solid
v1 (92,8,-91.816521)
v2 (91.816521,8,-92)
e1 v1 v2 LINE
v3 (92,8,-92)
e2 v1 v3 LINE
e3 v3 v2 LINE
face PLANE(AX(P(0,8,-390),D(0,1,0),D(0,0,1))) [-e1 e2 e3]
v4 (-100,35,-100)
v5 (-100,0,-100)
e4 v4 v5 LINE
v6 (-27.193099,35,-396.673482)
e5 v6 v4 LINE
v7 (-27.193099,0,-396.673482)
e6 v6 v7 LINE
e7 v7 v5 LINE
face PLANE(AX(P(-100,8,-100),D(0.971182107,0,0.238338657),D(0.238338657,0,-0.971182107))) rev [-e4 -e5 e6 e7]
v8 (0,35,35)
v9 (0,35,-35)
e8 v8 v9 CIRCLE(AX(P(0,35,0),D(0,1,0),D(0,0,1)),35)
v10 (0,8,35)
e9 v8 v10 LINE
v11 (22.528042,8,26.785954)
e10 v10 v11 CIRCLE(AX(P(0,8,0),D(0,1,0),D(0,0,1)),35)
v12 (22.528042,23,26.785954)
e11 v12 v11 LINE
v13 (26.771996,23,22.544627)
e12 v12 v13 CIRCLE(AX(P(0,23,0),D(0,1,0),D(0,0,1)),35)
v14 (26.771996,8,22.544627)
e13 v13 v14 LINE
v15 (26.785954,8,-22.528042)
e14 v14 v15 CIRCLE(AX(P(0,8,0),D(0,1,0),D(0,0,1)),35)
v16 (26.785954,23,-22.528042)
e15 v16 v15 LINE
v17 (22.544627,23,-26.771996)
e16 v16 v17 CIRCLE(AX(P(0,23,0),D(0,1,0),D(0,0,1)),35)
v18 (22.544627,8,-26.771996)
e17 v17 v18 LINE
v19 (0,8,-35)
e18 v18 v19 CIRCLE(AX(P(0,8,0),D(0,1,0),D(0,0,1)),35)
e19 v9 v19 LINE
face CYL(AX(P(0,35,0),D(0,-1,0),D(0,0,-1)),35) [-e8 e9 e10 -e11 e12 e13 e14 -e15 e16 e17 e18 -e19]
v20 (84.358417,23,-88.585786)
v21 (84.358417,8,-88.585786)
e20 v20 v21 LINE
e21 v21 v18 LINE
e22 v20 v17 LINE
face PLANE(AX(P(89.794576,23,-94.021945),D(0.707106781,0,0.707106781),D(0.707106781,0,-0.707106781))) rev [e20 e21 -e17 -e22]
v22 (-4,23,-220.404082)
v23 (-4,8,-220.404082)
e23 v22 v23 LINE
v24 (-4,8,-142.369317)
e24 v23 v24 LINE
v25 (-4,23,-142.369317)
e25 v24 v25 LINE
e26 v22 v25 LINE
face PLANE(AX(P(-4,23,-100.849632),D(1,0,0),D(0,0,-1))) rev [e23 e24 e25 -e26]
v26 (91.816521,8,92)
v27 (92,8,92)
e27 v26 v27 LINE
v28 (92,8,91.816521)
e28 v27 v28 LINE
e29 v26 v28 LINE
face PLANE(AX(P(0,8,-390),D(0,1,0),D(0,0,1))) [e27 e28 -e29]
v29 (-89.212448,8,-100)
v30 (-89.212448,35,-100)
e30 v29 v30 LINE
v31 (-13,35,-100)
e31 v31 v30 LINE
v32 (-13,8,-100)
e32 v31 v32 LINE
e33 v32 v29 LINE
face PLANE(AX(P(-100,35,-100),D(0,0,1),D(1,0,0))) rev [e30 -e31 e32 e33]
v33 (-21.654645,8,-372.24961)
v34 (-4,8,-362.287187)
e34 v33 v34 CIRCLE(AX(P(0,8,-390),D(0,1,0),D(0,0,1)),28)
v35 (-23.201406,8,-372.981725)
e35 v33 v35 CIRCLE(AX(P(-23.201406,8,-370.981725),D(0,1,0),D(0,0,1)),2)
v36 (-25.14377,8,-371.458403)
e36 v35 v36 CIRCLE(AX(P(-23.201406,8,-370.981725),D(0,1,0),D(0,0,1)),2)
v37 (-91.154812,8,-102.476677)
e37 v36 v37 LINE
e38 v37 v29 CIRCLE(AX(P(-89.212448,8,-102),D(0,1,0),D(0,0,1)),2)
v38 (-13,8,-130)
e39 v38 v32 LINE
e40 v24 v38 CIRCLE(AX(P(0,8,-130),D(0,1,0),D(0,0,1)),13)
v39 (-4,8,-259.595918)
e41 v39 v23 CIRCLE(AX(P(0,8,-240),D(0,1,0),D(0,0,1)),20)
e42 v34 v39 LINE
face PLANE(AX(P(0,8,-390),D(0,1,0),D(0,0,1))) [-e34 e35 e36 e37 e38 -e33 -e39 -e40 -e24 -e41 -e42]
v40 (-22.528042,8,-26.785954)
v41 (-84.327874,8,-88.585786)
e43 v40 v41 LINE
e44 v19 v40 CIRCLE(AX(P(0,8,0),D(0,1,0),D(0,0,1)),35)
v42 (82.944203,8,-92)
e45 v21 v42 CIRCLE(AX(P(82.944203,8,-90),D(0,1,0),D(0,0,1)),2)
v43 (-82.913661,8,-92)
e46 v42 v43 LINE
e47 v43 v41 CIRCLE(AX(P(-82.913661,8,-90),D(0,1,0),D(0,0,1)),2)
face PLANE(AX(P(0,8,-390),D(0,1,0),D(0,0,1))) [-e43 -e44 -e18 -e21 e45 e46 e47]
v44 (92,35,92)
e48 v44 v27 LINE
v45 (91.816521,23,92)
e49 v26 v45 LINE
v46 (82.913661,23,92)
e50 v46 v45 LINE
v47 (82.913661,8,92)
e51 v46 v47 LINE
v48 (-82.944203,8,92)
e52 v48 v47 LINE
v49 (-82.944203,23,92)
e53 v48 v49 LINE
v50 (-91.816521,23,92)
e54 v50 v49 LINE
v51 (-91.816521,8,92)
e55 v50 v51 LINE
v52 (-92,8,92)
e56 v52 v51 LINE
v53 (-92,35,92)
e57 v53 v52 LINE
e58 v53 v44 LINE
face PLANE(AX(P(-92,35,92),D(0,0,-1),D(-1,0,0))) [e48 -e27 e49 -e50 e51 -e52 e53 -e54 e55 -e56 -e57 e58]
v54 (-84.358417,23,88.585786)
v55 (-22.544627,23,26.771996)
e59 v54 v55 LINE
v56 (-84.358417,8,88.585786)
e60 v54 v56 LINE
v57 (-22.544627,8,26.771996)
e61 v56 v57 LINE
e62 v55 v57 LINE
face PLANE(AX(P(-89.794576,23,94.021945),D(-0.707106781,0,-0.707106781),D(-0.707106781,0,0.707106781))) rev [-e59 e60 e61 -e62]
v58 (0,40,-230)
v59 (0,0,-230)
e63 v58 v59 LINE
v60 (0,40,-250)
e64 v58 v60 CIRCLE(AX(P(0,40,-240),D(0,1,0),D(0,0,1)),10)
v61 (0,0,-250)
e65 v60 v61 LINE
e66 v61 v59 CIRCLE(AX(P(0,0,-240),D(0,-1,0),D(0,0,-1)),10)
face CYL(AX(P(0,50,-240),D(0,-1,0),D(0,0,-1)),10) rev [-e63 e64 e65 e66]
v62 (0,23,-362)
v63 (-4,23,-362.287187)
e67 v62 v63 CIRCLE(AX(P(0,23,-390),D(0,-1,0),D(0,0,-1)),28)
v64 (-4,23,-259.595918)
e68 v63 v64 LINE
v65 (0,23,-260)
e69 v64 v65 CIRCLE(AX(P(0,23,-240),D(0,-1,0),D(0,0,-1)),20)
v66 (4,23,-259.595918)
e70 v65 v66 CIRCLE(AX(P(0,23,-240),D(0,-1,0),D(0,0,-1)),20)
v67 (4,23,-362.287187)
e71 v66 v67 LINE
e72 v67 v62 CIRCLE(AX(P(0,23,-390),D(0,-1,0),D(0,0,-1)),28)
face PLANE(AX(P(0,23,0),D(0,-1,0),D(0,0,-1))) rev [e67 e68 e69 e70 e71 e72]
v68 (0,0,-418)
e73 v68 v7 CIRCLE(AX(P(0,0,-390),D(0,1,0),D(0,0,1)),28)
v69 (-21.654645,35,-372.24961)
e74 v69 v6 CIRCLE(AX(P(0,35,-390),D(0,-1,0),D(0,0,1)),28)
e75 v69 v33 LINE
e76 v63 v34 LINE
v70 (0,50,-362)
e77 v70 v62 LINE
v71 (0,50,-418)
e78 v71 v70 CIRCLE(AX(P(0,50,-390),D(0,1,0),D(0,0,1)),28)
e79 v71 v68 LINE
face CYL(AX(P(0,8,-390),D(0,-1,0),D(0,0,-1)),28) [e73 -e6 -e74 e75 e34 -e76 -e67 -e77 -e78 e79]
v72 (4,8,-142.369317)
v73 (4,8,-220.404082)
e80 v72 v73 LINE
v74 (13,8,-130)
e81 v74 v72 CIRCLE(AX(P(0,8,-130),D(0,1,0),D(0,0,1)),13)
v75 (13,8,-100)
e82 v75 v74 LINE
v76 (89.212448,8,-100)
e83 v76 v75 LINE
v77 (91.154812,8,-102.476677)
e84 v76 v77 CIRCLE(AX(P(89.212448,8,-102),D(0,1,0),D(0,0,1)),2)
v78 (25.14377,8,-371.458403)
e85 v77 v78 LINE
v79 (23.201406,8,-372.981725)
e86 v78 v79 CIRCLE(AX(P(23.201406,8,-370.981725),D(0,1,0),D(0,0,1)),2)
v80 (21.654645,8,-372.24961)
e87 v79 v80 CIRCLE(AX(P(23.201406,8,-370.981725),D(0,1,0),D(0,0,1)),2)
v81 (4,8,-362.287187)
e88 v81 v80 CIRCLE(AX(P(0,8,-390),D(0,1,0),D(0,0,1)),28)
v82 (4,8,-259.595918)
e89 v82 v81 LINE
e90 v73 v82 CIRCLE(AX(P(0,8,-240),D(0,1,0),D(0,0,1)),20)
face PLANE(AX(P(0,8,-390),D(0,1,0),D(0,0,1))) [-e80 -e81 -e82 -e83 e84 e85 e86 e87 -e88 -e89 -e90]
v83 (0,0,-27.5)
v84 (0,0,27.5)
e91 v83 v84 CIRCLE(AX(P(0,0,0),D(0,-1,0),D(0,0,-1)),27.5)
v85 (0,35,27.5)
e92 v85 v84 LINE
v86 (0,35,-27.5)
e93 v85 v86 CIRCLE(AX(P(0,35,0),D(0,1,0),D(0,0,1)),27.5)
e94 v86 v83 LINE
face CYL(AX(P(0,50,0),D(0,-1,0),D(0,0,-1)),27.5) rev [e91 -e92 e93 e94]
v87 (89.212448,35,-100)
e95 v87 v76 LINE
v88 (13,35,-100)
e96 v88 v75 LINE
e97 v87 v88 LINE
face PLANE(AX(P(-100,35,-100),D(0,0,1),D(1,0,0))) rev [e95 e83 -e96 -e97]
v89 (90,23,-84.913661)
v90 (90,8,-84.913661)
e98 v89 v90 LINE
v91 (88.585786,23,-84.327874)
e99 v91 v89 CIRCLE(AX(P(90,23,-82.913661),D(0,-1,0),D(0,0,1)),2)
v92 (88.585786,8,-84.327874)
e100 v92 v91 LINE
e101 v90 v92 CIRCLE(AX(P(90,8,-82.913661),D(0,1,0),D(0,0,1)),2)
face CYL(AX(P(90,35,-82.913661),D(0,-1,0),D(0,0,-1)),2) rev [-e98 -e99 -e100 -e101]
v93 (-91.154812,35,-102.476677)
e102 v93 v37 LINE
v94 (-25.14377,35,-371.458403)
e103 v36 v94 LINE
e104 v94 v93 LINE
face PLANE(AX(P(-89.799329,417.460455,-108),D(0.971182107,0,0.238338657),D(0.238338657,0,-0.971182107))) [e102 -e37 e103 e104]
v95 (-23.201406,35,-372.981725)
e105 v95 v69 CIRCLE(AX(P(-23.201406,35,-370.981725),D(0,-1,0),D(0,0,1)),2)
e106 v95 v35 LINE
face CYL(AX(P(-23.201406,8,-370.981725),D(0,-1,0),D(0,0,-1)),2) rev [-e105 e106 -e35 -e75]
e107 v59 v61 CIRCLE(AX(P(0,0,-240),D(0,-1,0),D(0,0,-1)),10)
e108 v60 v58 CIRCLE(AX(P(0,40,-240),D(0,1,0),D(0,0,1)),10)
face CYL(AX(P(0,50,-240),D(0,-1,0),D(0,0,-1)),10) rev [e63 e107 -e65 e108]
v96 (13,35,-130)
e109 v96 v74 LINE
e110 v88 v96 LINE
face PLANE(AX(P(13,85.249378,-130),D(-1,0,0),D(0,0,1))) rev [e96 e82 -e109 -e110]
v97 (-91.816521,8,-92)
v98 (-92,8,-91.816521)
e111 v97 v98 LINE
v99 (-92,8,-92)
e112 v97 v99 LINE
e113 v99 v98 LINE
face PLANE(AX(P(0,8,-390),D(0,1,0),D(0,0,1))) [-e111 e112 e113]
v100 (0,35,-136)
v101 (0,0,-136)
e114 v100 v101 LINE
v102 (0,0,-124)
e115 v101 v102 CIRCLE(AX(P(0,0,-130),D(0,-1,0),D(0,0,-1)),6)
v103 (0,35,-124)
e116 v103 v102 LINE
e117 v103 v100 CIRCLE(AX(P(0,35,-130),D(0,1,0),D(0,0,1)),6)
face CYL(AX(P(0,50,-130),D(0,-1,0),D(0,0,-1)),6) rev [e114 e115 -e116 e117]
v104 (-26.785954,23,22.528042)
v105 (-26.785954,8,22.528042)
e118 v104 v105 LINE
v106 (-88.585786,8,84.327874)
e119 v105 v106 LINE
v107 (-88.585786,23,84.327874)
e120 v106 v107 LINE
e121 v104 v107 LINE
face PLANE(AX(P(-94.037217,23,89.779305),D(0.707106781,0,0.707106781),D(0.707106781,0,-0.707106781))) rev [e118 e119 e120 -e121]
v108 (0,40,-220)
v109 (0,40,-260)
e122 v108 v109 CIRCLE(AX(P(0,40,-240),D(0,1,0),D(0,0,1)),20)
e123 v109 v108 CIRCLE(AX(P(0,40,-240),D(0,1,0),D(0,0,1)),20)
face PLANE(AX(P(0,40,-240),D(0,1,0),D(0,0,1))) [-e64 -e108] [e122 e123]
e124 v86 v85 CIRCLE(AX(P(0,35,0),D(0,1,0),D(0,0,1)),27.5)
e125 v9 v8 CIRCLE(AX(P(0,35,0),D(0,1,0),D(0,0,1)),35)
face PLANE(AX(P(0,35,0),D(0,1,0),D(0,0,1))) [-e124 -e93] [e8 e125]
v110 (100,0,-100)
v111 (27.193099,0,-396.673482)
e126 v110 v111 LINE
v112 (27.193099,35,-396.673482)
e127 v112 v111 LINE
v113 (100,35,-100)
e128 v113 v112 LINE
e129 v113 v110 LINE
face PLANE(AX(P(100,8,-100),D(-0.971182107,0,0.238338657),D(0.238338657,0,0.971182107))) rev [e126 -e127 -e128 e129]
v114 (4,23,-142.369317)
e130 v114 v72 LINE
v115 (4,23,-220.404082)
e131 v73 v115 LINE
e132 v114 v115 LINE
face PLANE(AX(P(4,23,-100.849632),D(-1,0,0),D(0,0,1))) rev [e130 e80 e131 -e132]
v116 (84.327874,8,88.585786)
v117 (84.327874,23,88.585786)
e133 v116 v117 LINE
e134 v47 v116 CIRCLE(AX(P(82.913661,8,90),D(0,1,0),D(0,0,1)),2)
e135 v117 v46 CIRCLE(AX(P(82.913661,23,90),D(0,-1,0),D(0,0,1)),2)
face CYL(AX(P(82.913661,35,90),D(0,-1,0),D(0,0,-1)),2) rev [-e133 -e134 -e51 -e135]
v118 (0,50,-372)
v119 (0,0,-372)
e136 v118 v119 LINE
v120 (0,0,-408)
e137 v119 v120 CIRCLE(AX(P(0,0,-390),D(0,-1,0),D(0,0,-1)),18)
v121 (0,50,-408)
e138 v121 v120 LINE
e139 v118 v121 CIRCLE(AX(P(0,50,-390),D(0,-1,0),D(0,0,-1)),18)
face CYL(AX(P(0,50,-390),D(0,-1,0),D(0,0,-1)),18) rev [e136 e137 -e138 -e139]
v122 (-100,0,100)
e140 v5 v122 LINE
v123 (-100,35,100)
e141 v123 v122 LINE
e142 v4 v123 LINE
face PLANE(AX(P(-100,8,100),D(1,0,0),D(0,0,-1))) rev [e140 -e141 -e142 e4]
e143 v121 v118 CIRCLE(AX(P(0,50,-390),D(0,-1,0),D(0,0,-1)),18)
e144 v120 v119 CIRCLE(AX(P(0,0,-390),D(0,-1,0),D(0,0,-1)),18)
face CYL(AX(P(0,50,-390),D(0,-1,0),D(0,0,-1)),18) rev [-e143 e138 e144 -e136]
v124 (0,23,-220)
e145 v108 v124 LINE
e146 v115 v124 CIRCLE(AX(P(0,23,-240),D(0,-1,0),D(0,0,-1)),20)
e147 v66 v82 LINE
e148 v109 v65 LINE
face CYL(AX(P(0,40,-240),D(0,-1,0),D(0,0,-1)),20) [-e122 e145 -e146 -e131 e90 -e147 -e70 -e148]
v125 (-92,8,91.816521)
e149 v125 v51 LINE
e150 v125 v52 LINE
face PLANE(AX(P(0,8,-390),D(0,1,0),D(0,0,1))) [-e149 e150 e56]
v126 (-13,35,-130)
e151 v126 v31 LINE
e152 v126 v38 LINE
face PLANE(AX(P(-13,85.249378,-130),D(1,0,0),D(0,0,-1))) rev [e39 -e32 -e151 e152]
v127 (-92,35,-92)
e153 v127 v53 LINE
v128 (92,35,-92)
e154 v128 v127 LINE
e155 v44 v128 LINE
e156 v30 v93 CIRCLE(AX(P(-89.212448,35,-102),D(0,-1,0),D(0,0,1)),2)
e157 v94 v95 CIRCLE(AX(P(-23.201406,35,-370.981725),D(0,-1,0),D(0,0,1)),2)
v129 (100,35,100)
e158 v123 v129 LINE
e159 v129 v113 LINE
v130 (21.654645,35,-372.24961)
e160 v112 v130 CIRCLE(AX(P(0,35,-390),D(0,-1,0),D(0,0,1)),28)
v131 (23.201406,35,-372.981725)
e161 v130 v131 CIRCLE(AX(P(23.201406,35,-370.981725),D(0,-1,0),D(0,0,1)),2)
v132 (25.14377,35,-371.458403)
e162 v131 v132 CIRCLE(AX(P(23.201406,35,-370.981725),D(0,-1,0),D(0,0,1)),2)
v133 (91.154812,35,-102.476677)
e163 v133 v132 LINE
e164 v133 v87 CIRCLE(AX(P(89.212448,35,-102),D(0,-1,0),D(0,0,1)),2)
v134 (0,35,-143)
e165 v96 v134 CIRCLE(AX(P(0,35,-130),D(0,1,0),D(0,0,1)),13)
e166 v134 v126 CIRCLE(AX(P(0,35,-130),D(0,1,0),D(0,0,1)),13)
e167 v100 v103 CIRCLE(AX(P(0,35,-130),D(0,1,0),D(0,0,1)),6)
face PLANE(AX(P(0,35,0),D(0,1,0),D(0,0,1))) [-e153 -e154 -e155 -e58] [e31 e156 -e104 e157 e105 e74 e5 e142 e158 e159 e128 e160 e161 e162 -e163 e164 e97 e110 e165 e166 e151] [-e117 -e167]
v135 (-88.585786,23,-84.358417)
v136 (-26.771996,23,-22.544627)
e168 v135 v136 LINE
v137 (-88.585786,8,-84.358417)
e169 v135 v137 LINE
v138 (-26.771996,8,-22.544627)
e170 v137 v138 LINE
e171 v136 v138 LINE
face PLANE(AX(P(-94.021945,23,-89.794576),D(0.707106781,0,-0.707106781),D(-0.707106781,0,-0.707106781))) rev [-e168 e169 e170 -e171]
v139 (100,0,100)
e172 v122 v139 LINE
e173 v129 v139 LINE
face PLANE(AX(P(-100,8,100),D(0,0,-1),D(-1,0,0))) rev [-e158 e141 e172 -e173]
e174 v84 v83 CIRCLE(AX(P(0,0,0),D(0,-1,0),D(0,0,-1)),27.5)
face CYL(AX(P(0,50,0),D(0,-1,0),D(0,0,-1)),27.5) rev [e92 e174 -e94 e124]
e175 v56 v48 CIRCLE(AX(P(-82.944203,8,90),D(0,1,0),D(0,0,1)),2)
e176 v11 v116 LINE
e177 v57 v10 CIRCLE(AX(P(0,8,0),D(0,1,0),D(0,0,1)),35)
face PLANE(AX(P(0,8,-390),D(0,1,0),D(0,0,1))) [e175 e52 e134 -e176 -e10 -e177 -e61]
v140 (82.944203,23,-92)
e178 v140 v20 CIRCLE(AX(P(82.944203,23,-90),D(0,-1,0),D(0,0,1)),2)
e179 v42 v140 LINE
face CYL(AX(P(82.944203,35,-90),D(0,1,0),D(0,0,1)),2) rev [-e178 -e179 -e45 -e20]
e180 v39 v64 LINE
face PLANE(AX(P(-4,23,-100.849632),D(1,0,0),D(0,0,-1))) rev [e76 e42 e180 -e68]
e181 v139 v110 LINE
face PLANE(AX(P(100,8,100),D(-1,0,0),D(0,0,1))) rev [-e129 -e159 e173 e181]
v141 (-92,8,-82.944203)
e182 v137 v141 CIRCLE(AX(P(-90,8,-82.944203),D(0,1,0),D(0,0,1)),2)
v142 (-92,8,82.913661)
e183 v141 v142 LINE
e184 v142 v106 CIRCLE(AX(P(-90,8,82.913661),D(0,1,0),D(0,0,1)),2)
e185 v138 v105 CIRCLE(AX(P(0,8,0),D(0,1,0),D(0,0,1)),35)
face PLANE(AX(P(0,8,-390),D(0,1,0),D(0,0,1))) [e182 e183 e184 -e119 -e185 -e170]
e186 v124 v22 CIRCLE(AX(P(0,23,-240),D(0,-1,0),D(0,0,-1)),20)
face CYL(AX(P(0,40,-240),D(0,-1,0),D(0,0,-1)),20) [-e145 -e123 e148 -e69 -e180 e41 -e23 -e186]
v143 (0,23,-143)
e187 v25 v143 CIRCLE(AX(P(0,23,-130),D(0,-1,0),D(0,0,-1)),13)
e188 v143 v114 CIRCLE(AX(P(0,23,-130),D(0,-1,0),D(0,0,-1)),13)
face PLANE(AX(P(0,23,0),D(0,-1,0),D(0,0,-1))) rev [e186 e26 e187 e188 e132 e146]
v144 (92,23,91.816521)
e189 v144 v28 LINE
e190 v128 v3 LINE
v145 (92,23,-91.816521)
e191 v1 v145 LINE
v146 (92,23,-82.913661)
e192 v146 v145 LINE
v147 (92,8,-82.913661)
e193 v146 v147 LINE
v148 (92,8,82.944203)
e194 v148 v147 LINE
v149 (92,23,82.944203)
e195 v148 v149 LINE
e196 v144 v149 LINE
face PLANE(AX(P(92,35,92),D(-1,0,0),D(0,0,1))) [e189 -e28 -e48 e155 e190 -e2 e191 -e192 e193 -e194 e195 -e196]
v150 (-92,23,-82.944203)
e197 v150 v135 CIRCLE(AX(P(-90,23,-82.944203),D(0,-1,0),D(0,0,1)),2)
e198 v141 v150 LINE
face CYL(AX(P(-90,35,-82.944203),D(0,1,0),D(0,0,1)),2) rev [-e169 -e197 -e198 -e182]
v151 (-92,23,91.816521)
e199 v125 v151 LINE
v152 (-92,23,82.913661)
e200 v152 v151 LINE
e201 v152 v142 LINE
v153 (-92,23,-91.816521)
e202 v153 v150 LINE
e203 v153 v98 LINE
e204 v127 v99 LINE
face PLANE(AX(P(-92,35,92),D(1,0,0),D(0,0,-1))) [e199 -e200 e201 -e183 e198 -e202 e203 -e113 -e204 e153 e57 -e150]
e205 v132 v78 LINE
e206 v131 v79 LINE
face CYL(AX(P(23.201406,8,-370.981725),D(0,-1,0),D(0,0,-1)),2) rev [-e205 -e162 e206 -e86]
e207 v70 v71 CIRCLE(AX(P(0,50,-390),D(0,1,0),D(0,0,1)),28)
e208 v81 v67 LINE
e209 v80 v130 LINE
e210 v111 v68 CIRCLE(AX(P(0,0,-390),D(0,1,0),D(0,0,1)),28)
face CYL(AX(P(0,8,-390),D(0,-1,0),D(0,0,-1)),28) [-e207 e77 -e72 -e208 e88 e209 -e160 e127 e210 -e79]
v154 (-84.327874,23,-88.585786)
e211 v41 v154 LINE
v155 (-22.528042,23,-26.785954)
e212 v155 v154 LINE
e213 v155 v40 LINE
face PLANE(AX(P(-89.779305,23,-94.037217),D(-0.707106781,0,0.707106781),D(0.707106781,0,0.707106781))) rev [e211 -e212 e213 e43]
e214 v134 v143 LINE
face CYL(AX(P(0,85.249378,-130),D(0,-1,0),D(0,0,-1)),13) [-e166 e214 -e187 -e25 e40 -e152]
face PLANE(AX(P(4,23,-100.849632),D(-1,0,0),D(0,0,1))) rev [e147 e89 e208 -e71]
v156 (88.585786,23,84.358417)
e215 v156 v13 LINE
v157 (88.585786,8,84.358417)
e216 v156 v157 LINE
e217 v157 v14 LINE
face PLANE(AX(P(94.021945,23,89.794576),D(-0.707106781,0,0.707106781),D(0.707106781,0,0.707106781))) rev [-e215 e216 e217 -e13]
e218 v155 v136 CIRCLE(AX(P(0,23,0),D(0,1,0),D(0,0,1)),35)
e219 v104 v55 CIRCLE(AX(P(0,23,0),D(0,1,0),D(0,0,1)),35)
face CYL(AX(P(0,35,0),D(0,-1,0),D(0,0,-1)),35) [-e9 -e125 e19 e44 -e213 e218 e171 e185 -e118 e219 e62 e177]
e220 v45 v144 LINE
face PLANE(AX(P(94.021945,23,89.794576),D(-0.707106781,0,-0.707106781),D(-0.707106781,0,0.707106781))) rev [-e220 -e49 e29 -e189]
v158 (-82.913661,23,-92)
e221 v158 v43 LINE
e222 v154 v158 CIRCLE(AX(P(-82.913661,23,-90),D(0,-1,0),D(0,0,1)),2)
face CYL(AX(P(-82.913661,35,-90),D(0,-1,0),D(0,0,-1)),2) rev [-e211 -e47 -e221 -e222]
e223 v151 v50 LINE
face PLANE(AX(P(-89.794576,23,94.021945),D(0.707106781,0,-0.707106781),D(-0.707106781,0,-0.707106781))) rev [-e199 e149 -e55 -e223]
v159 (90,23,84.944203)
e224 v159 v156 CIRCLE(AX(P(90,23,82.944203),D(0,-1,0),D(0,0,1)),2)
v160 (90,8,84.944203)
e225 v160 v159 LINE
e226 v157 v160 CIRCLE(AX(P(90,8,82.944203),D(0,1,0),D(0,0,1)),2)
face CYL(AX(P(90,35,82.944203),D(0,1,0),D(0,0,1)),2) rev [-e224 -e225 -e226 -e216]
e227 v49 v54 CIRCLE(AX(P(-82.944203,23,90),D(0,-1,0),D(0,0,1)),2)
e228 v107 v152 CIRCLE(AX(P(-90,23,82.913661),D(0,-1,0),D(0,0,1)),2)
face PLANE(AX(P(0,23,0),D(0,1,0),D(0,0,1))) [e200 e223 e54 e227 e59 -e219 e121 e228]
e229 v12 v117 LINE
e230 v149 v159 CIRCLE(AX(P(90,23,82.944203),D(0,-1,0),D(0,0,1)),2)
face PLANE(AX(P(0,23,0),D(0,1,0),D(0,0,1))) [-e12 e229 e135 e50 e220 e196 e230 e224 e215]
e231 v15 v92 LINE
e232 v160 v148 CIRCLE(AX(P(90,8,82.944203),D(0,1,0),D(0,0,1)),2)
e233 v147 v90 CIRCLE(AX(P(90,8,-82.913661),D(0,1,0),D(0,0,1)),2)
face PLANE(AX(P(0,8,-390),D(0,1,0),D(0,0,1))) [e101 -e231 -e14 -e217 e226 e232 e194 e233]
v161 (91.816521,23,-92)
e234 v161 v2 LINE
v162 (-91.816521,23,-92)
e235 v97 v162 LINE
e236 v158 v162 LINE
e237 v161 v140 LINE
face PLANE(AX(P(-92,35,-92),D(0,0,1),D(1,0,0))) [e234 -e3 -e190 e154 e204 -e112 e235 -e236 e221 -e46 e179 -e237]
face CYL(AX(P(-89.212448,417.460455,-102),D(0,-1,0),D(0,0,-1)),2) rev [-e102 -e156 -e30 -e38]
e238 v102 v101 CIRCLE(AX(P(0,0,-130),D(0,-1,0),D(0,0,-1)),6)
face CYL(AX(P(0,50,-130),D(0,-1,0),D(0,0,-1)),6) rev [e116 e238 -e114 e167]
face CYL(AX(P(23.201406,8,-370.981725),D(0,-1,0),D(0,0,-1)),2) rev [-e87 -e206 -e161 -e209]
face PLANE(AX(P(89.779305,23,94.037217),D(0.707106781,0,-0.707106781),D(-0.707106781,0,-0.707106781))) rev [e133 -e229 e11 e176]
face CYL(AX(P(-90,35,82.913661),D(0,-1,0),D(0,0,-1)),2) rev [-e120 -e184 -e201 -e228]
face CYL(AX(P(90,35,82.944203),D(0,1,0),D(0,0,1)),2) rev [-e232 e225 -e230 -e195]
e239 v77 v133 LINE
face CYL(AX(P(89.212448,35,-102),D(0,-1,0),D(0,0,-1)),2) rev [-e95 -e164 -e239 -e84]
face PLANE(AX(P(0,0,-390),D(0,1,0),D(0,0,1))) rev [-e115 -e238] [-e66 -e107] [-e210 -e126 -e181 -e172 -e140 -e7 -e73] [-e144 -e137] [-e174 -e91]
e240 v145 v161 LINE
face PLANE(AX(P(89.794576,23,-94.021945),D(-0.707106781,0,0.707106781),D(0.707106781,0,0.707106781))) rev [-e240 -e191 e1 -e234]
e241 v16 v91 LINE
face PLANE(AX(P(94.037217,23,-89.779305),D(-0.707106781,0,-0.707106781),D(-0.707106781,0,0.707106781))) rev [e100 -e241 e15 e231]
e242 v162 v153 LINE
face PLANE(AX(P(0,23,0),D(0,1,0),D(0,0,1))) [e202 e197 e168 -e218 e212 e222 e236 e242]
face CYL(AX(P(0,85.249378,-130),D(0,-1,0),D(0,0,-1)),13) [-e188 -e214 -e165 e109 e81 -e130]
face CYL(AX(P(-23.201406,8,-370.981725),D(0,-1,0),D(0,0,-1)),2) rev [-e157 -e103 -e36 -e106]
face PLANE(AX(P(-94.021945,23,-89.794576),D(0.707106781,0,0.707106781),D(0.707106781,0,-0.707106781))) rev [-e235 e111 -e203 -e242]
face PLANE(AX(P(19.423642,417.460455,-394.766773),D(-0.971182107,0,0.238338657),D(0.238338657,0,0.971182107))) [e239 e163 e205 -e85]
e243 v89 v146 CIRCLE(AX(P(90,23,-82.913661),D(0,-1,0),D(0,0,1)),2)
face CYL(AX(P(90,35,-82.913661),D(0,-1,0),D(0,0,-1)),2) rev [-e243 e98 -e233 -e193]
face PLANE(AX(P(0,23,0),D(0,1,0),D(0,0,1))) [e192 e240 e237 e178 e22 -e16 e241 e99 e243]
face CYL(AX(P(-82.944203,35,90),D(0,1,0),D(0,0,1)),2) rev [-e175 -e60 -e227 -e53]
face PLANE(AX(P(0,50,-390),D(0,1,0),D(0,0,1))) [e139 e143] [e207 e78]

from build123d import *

# Parameters (mm, degrees)
BASE_PLATE_8MM_DEPTH      = 8
PERIMETER_WALL_SKETCH_W   = 200
PERIMETER_WALL_SKETCH_H   = 200
PERIMETER_WALL_SKETCH_W_2 = 184
PERIMETER_WALL_SKETCH_H_2 = 184
PERIMETER_WALL_DEPTH      = 27
CROSS_WALL_DEPTH          = 27
TIP_BOSS_SKETCH_R         = 28
ARM_TIP_BOSS_DEPTH        = 42
ARM_PAD_130X26_DEPTH      = 27
HUB_BOSS_SKETCH_R         = 35
HUB_BOSS_70_DEPTH         = 27
MID_BOSS_SKETCH_R         = 20
MID_ARM_BOSS_40_DEPTH     = 32
HUB_GUSSET_RIBS_4X_DEPTH  = 15
WALL_AND_RIB_FILLETS_R2_R = 2
ARM_RIBS_SKETCH_W         = 8
ARM_RIBS_SKETCH_H         = 265.57093639
ARM_GUSSET_RIBS_DEPTH     = 15
BOSS_BORES_SKETCH_R       = 27.5
BOSS_BORES_SKETCH_R_2     = 6
BOSS_BORES_SKETCH_R_3     = 10
BOSS_BORES_SKETCH_R_4     = 18
BOSS_BORES_DEPTH          = 433.693887177


with BuildPart() as part:
    # Base Plate Sketch → Base Plate 8mm (new body)
    with BuildSketch(Plane(origin=(0, 0, 0), x_dir=(1, 0, 0), z_dir=(0, 1, 0))):
        with BuildLine():
            Line((-100, -100), (100, -100))
            Line((100, -100), (100, 100))
            Line((100, 100), (27.193098987, 396.673482409))
            ThreePointArc((27.193098987, 396.673482409), (0, 418), (-27.193098987, 396.673482409))
            Line((-27.193098987, 396.673482409), (-100, 100))
            Line((-100, 100), (-100, -100))
        make_face()
    extrude(amount=BASE_PLATE_8MM_DEPTH)

    # Perimeter Wall Sketch → Perimeter Wall (add)
    with BuildSketch(Plane(origin=(0, 8, 0), x_dir=(1, 0, 0), z_dir=(0, 1, 0))):
        Rectangle(PERIMETER_WALL_SKETCH_W, PERIMETER_WALL_SKETCH_H)
        Rectangle(PERIMETER_WALL_SKETCH_W_2, PERIMETER_WALL_SKETCH_H_2, mode=Mode.SUBTRACT)
    extrude(amount=PERIMETER_WALL_DEPTH)

    # Cross Wall Sketch → Cross Wall (add)
    with BuildSketch(Plane(origin=(0, 8, 0), x_dir=(1, 0, 0), z_dir=(0, 1, 0))):
        with BuildLine():
            Line((-100, 100), (-27.193098987, 396.673482409))
            ThreePointArc((-27.193098987, 396.673482409), (0, 418), (27.193098987, 396.673482409))
            Line((27.193098987, 396.673482409), (100, 100))
            Line((100, 100), (100, 92))
            Line((100, 92), (-100, 92))
            Line((-100, 92), (-100, 100))
        make_face()
        with BuildLine():
            Line((-89.799328888, 108), (-19.423642134, 394.76677315))
            ThreePointArc((-19.423642134, 394.76677315), (0, 410), (19.423642134, 394.76677315))
            Line((19.423642134, 394.76677315), (89.799328888, 108))
            Line((89.799328888, 108), (91.762615945, 100))
            Line((91.762615945, 100), (-91.762615945, 100))
            Line((-91.762615945, 100), (-89.799328888, 108))
        make_face(mode=Mode.SUBTRACT)
    extrude(amount=CROSS_WALL_DEPTH)

    # Tip Boss Sketch → Arm Tip Boss (add)
    with BuildSketch(Plane(origin=(0, 8, 0), x_dir=(1, 0, 0), z_dir=(0, 1, 0))):
        with Locations(Location((0, 390, 0), (0, 0, 13.788507306))):
            Circle(TIP_BOSS_SKETCH_R)
    extrude(amount=ARM_TIP_BOSS_DEPTH)

    # Arm Pad Sketch → Arm Pad 130x26 (add)
    with BuildSketch(Plane(origin=(0, 8, 0), x_dir=(1, 0, 0), z_dir=(0, 1, 0))):
        with BuildLine():
            Line((-13, 130), (-13, 100))
            Line((-13, 100), (13, 100))
            Line((13, 100), (13, 130))
            ThreePointArc((13, 130), (0, 143), (-13, 130))
        make_face()
    extrude(amount=ARM_PAD_130X26_DEPTH)

    # Hub Boss Sketch → Hub Boss Ø70 (add)
    with BuildSketch(Plane(origin=(0, 8, 0), x_dir=(1, 0, 0), z_dir=(0, 1, 0))):
        with Locations(Location((0, 0, 0), (0, 0, 270))):
            Circle(HUB_BOSS_SKETCH_R)
    extrude(amount=HUB_BOSS_70_DEPTH)

    # Mid Boss Sketch → Mid Arm Boss Ø40 (add)
    with BuildSketch(Plane(origin=(0, 8, 0), x_dir=(1, 0, 0), z_dir=(0, 1, 0))):
        with Locations(Location((0, 240, 0), (0, 0, 270))):
            Circle(MID_BOSS_SKETCH_R)
    extrude(amount=MID_ARM_BOSS_40_DEPTH)

    # Hub Ribs Sketch → Hub Gusset Ribs 4x (add)
    with BuildSketch(Plane(origin=(0, 8, 0), x_dir=(1, 0, 0), z_dir=(0, 1, 0))):
        with BuildLine():
            Line((89.794575879, 94.021945277), (22.544627023, 26.771996421))
            ThreePointArc((22.544627023, 26.771996421), (0.010838319, 34.999998322), (-22.528041932, 26.785953907))
            Line((-22.528041932, 26.785953907), (-89.77930459, 94.037216566))
            Line((-89.77930459, 94.037216566), (-94.021945277, 89.794575879))
            Line((-94.021945277, 89.794575879), (-26.771996421, 22.544627023))
            ThreePointArc((-26.771996421, 22.544627023), (-34.999998322, 0.010838319), (-26.785953907, -22.528041932))
            Line((-26.785953907, -22.528041932), (-94.037216566, -89.77930459))
            Line((-94.037216566, -89.77930459), (-89.794575879, -94.021945277))
            Line((-89.794575879, -94.021945277), (-22.544627023, -26.771996421))
            ThreePointArc((-22.544627023, -26.771996421), (-0.010838319, -34.999998322), (22.528041932, -26.785953907))
            Line((22.528041932, -26.785953907), (89.77930459, -94.037216566))
            Line((89.77930459, -94.037216566), (94.021945277, -89.794575879))
            Line((94.021945277, -89.794575879), (26.771996421, -22.544627023))
            ThreePointArc((26.771996421, -22.544627023), (34.999998322, -0.010838319), (26.785953907, 22.528041932))
            Line((26.785953907, 22.528041932), (94.037216566, 89.77930459))
            Line((94.037216566, 89.77930459), (89.794575879, 94.021945277))
        make_face()
    extrude(amount=HUB_GUSSET_RIBS_4X_DEPTH)

    # Wall and Rib Fillets R2
    wall_and_rib_fillets_r2_edges = [part.edges().sort_by_distance(p)[0] for p in [
        (87.772630602, 15.5, -92),
        (-87.742088024, 15.5, -92),
        (-92, 15.5, -87.772630602),
        (-92, 15.5, 87.742088024),
        (-87.772630602, 15.5, 92),
        (87.742088024, 15.5, 92),
        (92, 15.5, 87.772630602),
        (92, 15.5, -87.742088024),
        (-91.762615945, 21.5, -100),
        (91.762615945, 21.5, -100),
        (24.094106908, 21.5, -375.73556828),
        (-24.094106908, 21.5, -375.73556828),
    ]]
    fillet(wall_and_rib_fillets_r2_edges, radius=WALL_AND_RIB_FILLETS_R2_R)

    # Arm Ribs Sketch → Arm Gusset Ribs (add)
    with BuildSketch(Plane(origin=(0, 8, 0), x_dir=(1, 0, 0), z_dir=(0, 1, 0))):
        with Locations((0, 233.635099789)):
            Rectangle(ARM_RIBS_SKETCH_W, ARM_RIBS_SKETCH_H)
    extrude(amount=ARM_GUSSET_RIBS_DEPTH)

    # Boss Bores Sketch → Boss Bores (cut, through all)
    with BuildSketch(Plane.XZ):
        with Locations(Location((0, 0, 0), (0, 0, 270))):
            Circle(BOSS_BORES_SKETCH_R)
        with Locations(Location((0, -130, 0), (0, 0, 270))):
            Circle(BOSS_BORES_SKETCH_R_2)
        with Locations(Location((0, -240, 0), (0, 0, 270))):
            Circle(BOSS_BORES_SKETCH_R_3)
        with Locations(Location((0, -390, 0), (0, 0, 270))):
            Circle(BOSS_BORES_SKETCH_R_4)
    extrude(amount=-BOSS_BORES_DEPTH, mode=Mode.SUBTRACT)


solid = part.part
